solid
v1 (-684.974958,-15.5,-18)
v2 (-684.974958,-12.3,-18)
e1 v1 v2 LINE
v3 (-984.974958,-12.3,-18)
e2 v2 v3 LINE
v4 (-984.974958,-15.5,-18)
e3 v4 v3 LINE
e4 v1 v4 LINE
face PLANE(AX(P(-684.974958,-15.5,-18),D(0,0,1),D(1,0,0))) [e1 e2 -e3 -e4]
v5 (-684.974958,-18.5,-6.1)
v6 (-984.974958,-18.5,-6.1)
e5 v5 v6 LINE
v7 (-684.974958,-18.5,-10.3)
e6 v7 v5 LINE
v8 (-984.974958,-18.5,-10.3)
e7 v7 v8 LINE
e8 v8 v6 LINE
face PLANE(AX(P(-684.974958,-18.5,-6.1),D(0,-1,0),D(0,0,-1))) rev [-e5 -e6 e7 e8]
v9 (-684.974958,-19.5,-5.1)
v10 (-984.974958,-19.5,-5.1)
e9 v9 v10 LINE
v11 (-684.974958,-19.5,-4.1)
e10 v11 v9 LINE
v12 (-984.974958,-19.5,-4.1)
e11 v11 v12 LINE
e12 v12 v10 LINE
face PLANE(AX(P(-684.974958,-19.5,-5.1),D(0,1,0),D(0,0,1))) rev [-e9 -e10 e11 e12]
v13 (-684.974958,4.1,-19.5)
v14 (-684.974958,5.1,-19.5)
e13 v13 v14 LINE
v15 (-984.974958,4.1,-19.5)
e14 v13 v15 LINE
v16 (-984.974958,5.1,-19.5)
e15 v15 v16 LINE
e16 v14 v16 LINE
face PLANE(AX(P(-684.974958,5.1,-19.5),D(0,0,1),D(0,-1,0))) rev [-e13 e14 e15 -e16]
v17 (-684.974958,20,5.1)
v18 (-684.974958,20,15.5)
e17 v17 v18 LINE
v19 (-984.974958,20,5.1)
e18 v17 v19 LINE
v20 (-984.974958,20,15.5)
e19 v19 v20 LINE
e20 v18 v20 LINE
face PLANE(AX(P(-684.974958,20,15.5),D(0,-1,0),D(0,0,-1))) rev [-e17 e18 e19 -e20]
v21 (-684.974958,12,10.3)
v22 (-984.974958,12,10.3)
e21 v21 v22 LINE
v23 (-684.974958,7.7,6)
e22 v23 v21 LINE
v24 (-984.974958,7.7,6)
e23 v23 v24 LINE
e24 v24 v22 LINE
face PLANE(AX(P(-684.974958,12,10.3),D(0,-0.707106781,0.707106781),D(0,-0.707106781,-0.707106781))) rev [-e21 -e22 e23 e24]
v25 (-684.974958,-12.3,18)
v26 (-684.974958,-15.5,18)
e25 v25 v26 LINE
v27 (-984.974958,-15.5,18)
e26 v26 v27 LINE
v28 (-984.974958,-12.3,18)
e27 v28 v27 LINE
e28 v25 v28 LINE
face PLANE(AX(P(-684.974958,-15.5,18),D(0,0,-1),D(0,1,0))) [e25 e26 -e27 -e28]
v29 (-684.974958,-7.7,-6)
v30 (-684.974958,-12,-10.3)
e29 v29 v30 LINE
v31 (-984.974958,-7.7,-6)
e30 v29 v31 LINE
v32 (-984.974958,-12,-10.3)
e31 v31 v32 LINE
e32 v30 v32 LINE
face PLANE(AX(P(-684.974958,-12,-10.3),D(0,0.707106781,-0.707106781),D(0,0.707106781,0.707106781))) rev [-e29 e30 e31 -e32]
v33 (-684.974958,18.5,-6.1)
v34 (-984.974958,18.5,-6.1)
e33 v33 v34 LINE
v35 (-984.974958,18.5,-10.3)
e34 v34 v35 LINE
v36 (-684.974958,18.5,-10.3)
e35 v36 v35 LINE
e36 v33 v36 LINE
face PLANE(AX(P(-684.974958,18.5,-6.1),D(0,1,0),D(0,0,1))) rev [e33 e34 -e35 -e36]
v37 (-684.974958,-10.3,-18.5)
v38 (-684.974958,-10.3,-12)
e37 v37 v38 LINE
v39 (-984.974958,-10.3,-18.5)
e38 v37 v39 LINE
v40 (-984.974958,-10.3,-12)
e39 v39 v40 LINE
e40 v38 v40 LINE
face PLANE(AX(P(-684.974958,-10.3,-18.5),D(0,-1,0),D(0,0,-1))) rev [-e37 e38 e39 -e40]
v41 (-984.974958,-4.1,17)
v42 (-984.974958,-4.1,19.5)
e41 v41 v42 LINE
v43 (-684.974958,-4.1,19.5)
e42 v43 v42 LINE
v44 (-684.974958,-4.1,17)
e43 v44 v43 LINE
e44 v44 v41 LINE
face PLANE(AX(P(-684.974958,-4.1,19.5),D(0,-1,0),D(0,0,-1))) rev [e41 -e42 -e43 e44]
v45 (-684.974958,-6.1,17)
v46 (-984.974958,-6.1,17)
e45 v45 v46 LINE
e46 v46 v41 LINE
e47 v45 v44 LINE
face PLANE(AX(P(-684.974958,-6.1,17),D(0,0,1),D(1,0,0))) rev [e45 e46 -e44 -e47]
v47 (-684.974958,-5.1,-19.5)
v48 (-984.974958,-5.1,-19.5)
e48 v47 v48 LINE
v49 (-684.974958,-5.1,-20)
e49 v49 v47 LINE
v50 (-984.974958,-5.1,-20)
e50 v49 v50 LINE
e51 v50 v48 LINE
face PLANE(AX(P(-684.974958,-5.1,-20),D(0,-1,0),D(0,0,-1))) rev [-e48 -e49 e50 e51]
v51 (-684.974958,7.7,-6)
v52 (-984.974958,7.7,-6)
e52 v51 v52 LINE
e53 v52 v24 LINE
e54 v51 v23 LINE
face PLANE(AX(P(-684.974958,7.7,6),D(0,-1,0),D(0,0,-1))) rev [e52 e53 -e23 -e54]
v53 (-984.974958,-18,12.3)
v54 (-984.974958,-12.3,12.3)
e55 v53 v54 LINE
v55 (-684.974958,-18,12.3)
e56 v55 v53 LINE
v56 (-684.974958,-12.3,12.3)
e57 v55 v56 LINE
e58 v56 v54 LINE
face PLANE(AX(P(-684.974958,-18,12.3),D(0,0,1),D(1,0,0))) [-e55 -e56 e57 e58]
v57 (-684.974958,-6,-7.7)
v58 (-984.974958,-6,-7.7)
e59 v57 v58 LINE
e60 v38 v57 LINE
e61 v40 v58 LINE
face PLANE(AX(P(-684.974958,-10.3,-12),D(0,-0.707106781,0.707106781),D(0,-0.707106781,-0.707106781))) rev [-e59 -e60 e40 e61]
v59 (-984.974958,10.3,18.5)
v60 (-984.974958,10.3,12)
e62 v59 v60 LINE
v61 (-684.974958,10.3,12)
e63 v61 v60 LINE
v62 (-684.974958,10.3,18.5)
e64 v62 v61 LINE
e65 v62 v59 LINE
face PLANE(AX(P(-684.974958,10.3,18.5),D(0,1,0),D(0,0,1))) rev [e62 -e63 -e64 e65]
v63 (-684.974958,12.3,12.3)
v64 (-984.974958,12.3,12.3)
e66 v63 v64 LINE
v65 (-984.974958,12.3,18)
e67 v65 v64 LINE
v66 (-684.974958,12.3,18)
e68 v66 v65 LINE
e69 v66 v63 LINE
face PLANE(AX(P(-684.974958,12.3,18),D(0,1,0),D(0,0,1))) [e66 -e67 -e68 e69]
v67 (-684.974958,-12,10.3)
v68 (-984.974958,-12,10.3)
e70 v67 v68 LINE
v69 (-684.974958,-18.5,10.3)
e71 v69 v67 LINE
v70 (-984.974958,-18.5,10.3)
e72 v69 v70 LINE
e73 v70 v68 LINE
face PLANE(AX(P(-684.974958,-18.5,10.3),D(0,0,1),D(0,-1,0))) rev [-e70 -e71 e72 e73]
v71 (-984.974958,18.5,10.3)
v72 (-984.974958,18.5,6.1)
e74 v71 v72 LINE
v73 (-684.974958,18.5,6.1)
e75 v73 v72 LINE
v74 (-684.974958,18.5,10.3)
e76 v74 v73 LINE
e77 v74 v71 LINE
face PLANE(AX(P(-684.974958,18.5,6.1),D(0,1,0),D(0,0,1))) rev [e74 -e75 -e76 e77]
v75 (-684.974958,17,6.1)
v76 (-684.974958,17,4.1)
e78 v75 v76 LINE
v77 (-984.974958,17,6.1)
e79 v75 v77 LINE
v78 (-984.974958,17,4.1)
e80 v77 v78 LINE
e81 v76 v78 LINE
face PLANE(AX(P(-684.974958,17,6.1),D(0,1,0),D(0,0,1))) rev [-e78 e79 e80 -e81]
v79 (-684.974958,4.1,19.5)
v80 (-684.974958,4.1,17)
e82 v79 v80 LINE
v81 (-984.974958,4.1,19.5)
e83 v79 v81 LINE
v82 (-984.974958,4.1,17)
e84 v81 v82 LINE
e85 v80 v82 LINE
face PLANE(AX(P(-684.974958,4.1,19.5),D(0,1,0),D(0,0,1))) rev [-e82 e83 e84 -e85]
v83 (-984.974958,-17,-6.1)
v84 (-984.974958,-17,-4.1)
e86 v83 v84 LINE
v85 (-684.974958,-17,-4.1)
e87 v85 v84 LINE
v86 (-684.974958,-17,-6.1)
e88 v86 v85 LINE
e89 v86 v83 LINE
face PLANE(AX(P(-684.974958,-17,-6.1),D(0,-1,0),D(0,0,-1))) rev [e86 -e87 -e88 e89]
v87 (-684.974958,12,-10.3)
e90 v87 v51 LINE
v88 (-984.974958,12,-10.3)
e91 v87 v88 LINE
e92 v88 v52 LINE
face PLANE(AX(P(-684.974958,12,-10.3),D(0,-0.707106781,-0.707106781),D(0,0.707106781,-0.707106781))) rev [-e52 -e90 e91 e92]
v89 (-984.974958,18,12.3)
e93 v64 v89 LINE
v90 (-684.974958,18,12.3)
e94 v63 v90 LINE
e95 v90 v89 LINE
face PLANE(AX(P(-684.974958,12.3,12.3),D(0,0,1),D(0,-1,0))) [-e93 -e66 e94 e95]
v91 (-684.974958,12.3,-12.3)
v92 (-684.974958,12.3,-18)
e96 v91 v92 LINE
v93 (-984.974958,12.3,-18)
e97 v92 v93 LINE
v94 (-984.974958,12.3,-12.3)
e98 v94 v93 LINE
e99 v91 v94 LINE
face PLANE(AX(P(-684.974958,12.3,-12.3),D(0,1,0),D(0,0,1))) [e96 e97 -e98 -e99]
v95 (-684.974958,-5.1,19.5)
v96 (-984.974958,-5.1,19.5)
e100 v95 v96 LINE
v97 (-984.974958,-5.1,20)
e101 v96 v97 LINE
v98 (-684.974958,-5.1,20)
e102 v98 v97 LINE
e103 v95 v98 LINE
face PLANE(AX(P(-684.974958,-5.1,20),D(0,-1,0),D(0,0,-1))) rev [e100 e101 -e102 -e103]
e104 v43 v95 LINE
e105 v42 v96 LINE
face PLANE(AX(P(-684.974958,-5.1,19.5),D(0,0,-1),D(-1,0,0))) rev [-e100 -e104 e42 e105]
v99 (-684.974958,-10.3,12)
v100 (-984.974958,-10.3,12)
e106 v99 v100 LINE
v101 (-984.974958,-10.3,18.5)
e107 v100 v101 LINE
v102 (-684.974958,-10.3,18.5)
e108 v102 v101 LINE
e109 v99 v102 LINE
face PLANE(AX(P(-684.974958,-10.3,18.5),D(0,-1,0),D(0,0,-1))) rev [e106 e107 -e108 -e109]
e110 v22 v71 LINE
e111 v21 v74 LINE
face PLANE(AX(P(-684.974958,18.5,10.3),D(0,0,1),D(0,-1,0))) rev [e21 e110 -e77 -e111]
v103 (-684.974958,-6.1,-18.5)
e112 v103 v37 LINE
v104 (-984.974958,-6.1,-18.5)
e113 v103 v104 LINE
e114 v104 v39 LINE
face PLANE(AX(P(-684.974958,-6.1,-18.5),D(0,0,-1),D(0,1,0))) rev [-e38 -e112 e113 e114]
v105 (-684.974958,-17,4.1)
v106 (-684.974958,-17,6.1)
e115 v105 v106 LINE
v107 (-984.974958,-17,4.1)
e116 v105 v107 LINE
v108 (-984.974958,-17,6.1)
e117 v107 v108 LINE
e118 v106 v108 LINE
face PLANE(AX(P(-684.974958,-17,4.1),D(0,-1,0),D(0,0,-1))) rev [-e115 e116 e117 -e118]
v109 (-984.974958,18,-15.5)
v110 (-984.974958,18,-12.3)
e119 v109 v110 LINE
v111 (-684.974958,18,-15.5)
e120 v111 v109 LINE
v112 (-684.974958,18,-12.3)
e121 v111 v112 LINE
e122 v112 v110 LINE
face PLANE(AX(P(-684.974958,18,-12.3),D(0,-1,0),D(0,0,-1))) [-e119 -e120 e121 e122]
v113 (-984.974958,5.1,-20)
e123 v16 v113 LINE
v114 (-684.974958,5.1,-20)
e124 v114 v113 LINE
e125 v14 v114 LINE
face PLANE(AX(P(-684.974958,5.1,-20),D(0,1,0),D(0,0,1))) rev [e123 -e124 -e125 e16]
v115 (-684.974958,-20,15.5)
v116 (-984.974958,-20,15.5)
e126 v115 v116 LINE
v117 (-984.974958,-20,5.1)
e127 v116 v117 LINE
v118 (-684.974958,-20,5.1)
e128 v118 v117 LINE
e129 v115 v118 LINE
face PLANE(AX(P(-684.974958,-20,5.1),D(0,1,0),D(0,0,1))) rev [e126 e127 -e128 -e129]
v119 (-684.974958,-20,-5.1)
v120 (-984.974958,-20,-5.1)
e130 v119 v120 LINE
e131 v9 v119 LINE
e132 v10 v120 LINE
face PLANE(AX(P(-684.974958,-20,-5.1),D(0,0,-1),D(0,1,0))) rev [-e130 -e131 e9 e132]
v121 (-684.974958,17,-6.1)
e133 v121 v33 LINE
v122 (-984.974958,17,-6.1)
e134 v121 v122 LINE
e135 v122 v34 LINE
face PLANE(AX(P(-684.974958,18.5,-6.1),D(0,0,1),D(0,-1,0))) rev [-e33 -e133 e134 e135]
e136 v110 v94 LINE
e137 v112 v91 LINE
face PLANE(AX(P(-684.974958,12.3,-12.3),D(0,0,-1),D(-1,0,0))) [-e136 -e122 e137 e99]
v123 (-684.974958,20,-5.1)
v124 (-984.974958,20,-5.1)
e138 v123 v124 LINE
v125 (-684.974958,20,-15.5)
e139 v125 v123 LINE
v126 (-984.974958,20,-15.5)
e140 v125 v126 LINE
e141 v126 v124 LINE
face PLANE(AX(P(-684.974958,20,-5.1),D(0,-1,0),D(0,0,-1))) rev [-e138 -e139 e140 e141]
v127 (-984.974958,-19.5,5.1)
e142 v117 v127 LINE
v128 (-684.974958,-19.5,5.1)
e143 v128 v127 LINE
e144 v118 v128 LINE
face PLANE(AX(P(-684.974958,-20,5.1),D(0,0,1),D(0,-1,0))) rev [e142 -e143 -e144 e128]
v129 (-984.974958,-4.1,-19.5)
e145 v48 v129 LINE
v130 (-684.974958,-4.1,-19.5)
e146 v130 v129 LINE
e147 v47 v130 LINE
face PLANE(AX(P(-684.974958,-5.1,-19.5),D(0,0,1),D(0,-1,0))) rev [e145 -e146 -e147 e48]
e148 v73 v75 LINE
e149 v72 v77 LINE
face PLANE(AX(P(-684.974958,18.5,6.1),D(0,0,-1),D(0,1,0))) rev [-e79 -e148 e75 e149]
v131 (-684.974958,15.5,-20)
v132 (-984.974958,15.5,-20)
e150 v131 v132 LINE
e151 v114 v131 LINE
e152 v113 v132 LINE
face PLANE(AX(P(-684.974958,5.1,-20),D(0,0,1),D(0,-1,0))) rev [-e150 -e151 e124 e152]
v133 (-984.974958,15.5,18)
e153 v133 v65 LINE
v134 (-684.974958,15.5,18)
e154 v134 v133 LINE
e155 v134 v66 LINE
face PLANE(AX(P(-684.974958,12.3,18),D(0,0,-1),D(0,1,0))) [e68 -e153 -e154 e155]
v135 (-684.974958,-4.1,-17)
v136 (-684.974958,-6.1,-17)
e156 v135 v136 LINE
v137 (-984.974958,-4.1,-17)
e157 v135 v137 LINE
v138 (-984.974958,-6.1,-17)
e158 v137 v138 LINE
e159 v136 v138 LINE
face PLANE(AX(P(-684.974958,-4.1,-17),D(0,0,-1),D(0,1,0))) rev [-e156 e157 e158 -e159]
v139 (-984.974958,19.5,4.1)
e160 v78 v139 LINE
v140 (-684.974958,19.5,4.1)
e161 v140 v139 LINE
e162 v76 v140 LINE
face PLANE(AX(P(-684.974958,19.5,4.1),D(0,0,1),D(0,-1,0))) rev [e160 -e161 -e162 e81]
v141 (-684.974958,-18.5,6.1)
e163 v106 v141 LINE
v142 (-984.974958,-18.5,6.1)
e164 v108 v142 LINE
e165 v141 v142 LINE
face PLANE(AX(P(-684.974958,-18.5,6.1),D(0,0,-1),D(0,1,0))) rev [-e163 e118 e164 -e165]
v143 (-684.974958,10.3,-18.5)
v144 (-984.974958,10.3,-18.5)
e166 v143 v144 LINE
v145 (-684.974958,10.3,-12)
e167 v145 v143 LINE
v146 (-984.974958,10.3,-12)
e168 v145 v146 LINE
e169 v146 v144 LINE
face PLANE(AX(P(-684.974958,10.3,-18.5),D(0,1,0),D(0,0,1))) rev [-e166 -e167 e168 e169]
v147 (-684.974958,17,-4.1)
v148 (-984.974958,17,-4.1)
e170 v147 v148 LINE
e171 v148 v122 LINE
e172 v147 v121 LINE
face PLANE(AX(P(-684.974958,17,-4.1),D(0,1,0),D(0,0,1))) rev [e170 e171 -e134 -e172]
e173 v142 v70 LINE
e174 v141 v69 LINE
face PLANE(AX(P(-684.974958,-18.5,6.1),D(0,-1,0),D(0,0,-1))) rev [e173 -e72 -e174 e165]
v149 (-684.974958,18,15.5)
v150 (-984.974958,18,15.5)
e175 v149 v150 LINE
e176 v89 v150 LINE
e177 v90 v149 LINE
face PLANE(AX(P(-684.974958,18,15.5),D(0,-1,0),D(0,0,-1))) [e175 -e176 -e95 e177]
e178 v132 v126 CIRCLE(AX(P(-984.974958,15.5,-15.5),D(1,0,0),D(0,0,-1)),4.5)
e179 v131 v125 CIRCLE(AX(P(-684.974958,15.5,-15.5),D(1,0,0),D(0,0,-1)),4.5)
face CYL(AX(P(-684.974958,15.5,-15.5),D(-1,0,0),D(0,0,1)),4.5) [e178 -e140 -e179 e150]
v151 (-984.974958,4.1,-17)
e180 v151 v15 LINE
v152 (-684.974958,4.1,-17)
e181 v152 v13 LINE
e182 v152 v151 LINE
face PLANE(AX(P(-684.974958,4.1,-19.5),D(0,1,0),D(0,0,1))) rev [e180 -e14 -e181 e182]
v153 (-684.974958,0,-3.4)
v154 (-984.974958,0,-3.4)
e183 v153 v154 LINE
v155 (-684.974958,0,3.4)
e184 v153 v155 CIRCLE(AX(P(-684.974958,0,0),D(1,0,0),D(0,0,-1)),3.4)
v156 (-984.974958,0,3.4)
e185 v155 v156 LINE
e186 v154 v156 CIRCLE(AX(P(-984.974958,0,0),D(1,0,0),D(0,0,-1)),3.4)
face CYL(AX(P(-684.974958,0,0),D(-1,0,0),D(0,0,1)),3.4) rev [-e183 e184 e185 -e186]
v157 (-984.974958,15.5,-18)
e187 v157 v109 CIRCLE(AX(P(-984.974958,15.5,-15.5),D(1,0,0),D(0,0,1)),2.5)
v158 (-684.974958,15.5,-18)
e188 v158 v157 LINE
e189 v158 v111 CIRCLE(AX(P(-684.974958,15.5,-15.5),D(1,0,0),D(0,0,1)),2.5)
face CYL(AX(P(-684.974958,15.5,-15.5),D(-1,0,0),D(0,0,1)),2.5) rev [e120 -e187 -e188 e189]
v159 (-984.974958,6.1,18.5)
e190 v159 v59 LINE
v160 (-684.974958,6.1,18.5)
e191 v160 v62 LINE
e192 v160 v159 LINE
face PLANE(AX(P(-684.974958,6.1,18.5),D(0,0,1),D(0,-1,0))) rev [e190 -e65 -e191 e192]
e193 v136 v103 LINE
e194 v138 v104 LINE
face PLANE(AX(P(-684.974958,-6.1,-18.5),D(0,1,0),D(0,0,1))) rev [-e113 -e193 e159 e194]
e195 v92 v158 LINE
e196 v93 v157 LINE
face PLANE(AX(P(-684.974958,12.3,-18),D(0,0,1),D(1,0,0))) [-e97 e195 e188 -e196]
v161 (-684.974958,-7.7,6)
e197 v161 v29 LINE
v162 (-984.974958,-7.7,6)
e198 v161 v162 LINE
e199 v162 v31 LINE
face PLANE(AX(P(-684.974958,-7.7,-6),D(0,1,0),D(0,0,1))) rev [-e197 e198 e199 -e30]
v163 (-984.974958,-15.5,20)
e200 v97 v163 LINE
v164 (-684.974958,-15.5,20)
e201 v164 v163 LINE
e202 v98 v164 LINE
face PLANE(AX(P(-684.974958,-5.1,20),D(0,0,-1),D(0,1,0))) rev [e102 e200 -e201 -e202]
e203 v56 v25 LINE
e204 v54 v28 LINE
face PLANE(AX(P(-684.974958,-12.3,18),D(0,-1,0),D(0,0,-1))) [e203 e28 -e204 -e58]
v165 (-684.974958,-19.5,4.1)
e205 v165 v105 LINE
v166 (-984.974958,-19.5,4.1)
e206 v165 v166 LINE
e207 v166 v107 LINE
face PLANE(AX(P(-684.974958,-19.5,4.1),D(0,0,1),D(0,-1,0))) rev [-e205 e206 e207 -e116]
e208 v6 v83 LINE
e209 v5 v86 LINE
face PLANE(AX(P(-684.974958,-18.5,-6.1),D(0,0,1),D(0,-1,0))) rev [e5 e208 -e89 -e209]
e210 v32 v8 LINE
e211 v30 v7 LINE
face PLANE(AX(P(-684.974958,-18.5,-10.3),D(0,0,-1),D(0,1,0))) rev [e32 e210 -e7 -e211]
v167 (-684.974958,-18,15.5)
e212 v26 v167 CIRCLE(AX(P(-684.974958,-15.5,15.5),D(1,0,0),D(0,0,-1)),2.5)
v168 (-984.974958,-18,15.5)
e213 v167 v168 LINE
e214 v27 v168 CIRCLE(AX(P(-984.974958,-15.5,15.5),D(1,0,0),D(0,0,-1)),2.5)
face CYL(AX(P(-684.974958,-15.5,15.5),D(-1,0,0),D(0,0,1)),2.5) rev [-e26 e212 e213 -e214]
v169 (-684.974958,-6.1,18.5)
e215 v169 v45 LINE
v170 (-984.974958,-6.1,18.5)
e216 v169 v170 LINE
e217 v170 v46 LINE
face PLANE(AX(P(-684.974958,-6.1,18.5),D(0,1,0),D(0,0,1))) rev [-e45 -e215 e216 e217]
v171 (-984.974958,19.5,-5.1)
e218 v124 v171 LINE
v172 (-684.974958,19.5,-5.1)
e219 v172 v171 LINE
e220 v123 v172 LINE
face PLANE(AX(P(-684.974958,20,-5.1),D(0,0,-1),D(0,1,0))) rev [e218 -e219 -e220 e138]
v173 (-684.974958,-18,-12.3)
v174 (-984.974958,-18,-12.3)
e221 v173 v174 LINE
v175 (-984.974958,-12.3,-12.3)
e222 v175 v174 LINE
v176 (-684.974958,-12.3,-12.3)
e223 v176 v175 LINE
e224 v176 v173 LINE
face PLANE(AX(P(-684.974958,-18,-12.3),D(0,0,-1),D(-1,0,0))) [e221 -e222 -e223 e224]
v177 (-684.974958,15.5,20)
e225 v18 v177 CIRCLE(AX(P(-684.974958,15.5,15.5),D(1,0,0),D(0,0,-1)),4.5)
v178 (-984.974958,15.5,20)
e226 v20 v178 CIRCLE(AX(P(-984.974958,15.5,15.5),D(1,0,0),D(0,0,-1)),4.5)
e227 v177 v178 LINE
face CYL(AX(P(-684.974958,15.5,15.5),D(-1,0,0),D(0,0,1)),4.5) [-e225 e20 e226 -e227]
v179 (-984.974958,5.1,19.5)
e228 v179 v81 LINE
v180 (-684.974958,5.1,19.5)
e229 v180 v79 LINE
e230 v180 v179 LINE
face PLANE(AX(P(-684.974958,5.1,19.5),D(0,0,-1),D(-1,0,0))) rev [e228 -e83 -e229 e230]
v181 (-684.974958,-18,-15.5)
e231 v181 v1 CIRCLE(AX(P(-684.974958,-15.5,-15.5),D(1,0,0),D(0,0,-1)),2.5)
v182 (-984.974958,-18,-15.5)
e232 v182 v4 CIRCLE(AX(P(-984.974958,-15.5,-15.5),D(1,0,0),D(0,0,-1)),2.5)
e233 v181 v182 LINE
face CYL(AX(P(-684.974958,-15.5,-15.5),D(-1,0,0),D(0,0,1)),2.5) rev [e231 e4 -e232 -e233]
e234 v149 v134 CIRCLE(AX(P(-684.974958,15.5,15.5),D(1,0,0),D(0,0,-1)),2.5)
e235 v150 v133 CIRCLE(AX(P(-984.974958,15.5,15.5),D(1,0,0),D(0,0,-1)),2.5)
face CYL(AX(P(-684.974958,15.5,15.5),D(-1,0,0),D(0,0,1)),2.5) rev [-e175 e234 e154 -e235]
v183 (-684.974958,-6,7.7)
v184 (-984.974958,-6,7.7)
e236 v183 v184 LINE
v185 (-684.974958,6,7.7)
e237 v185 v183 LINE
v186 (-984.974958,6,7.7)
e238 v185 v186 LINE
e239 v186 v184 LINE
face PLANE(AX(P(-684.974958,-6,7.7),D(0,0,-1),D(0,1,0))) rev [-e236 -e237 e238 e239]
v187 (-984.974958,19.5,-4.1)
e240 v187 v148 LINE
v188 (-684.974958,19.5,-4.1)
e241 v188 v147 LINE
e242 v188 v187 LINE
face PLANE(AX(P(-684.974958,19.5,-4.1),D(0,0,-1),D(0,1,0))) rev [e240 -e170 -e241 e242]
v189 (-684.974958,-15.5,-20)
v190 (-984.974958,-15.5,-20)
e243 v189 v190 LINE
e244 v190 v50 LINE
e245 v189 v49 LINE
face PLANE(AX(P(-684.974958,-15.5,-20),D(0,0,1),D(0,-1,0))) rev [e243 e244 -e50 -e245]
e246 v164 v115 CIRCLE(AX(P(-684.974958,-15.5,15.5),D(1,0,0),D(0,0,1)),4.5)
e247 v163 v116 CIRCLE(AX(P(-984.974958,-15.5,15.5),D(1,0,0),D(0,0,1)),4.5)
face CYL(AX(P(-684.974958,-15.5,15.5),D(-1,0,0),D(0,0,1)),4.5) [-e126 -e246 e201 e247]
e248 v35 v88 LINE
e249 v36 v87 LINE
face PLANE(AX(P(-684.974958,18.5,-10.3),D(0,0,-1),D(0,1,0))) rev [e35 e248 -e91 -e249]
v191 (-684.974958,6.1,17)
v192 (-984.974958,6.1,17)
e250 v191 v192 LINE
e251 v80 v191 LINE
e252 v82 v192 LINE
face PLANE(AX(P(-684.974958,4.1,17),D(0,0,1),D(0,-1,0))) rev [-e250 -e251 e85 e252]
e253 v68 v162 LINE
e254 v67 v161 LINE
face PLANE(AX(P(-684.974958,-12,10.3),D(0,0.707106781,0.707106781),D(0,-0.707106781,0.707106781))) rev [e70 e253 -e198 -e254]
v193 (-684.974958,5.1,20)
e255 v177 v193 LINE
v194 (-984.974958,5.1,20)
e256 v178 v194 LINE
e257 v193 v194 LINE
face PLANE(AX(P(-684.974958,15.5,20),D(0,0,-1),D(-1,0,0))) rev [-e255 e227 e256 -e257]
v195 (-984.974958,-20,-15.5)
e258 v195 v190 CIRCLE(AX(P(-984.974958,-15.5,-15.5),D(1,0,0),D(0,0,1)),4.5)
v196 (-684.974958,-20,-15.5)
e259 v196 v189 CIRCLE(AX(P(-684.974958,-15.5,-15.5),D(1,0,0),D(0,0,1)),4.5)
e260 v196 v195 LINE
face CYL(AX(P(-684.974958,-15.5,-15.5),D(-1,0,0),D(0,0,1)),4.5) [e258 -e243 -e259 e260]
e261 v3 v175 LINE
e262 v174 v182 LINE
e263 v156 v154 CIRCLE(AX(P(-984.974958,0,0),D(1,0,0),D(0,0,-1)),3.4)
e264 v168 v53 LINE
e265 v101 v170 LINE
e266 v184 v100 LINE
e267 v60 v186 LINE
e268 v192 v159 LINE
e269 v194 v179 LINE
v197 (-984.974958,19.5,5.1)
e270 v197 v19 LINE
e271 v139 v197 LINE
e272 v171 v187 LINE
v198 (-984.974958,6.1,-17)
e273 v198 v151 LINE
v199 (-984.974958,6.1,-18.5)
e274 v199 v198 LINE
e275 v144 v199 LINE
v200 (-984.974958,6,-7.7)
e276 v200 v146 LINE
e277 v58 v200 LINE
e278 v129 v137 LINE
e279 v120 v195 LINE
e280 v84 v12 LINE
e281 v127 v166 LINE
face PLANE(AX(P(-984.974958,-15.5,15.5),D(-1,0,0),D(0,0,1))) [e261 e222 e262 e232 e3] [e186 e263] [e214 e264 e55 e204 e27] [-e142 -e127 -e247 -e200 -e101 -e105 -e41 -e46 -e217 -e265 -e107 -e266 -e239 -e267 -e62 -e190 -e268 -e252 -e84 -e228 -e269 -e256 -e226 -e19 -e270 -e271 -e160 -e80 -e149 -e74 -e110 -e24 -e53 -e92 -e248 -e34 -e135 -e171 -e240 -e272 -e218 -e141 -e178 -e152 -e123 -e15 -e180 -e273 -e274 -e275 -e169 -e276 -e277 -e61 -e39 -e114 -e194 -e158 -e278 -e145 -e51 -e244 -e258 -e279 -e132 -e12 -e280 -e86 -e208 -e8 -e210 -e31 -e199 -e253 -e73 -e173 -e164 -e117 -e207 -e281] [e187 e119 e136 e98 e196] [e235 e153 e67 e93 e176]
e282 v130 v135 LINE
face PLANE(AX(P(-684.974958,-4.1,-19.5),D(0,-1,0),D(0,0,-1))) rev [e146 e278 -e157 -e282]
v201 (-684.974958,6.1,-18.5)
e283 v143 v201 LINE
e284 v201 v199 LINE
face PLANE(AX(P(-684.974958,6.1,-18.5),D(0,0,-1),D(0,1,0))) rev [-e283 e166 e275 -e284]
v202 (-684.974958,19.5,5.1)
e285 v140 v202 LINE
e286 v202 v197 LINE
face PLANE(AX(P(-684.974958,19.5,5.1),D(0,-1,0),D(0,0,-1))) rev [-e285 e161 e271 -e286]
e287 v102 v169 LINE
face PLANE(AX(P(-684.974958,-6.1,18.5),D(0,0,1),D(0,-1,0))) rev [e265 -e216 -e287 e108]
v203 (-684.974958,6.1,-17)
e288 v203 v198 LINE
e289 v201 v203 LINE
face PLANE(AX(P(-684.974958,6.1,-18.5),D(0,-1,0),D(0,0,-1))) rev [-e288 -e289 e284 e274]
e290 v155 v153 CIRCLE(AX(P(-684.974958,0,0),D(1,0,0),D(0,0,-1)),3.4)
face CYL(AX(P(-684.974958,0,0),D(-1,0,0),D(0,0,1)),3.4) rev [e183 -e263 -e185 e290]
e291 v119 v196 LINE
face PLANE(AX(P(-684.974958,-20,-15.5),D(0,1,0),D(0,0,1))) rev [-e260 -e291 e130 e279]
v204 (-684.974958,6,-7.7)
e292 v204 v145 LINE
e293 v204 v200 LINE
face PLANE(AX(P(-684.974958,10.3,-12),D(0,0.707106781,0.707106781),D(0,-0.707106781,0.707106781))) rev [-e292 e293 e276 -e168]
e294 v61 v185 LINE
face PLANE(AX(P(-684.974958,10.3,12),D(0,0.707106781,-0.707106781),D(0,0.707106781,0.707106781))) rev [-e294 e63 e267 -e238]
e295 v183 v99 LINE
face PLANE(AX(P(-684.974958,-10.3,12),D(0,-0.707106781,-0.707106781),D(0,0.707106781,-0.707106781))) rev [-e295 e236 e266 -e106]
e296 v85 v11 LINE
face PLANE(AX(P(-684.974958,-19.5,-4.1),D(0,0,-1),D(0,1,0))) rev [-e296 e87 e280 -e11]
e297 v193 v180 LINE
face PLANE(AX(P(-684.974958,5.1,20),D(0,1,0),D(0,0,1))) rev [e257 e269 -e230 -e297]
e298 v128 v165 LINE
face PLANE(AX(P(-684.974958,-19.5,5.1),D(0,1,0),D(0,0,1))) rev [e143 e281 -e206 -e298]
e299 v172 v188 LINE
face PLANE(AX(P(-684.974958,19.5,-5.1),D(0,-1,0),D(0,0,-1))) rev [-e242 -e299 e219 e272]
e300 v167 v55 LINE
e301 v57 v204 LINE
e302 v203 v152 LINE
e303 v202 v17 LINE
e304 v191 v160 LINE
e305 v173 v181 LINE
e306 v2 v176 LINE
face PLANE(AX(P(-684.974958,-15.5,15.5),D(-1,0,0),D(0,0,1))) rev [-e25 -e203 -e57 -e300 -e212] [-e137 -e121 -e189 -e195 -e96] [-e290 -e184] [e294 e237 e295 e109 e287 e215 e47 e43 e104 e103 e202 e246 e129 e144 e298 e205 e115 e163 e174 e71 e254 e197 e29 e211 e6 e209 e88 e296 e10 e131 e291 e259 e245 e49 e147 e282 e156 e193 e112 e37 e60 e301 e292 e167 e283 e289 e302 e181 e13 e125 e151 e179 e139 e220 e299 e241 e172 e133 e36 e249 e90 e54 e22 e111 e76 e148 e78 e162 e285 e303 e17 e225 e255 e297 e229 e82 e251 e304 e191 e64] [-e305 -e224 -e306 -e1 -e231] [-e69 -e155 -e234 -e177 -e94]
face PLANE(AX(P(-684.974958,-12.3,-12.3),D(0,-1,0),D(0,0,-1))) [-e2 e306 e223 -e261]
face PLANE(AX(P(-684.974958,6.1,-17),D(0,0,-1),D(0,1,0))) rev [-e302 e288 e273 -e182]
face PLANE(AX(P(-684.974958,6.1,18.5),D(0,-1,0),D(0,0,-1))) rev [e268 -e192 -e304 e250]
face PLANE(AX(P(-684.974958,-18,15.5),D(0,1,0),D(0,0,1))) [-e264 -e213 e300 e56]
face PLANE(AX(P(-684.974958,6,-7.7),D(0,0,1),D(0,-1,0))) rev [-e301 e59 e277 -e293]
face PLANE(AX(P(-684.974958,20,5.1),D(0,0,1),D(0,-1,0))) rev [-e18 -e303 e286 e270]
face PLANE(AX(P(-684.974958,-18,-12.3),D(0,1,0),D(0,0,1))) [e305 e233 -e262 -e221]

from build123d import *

# Parameters (mm, degrees)
SKETCH1_R                                 = 3.4
ALUMINIUM_PROFILE_40_X_40B_X_R4_5_1_DEPTH = 300


with BuildPart() as part:
    # Sketch1 → Aluminium profile 40 X 40B X R4.5(1) (new body)
    with BuildSketch(Plane.YZ.offset(-984.974958264)):
        with BuildLine():
            Line((-5.1, 20), (-5.1, 19.5))
            Line((-5.1, 19.5), (-4.1, 19.5))
            Line((-4.1, 19.5), (-4.1, 17))
            Line((-4.1, 17), (-6.1, 17))
            Line((-6.1, 17), (-6.1, 18.5))
            Line((-6.1, 18.5), (-10.3, 18.5))
            Line((-10.3, 18.5), (-10.3, 12))
            Line((-10.3, 12), (-6, 7.7))
            Line((-6, 7.7), (6, 7.7))
            Line((6, 7.7), (10.3, 12))
            Line((10.3, 12), (10.3, 18.5))
            Line((10.3, 18.5), (6.1, 18.5))
            Line((6.1, 18.5), (6.1, 17))
            Line((6.1, 17), (4.1, 17))
            Line((4.1, 17), (4.1, 19.5))
            Line((4.1, 19.5), (5.1, 19.5))
            Line((5.1, 19.5), (5.1, 20))
            Line((5.1, 20), (15.5, 20))
            ThreePointArc((15.5, 20), (18.681980515, 18.681980515), (20, 15.5))
            Line((20, 15.5), (20, 5.1))
            Line((20, 5.1), (19.5, 5.1))
            Line((19.5, 5.1), (19.5, 4.1))
            Line((19.5, 4.1), (17, 4.1))
            Line((17, 4.1), (17, 6.1))
            Line((17, 6.1), (18.5, 6.1))
            Line((18.5, 6.1), (18.5, 10.3))
            Line((18.5, 10.3), (12, 10.3))
            Line((12, 10.3), (7.7, 6))
            Line((7.7, 6), (7.7, -6))
            Line((7.7, -6), (12, -10.3))
            Line((12, -10.3), (18.5, -10.3))
            Line((18.5, -10.3), (18.5, -6.1))
            Line((18.5, -6.1), (17, -6.1))
            Line((17, -6.1), (17, -4.1))
            Line((17, -4.1), (19.5, -4.1))
            Line((19.5, -4.1), (19.5, -5.1))
            Line((19.5, -5.1), (20, -5.1))
            Line((20, -5.1), (20, -15.5))
            ThreePointArc((20, -15.5), (18.681980515, -18.681980515), (15.5, -20))
            Line((15.5, -20), (5.1, -20))
            Line((5.1, -20), (5.1, -19.5))
            Line((5.1, -19.5), (4.1, -19.5))
            Line((4.1, -19.5), (4.1, -17))
            Line((4.1, -17), (6.1, -17))
            Line((6.1, -17), (6.1, -18.5))
            Line((6.1, -18.5), (10.3, -18.5))
            Line((10.3, -18.5), (10.3, -12))
            Line((10.3, -12), (6, -7.7))
            Line((6, -7.7), (-6, -7.7))
            Line((-6, -7.7), (-10.3, -12))
            Line((-10.3, -12), (-10.3, -18.5))
            Line((-10.3, -18.5), (-6.1, -18.5))
            Line((-6.1, -18.5), (-6.1, -17))
            Line((-6.1, -17), (-4.1, -17))
            Line((-4.1, -17), (-4.1, -19.5))
            Line((-4.1, -19.5), (-5.1, -19.5))
            Line((-5.1, -19.5), (-5.1, -20))
            Line((-5.1, -20), (-15.5, -20))
            ThreePointArc((-15.5, -20), (-18.681980515, -18.681980515), (-20, -15.5))
            Line((-20, -15.5), (-20, -5.1))
            Line((-20, -5.1), (-19.5, -5.1))
            Line((-19.5, -5.1), (-19.5, -4.1))
            Line((-19.5, -4.1), (-17, -4.1))
            Line((-17, -4.1), (-17, -6.1))
            Line((-17, -6.1), (-18.5, -6.1))
            Line((-18.5, -6.1), (-18.5, -10.3))
            Line((-18.5, -10.3), (-12, -10.3))
            Line((-12, -10.3), (-7.7, -6))
            Line((-7.7, -6), (-7.7, 6))
            Line((-7.7, 6), (-12, 10.3))
            Line((-12, 10.3), (-18.5, 10.3))
            Line((-18.5, 10.3), (-18.5, 6.1))
            Line((-18.5, 6.1), (-17, 6.1))
            Line((-17, 6.1), (-17, 4.1))
            Line((-17, 4.1), (-19.5, 4.1))
            Line((-19.5, 4.1), (-19.5, 5.1))
            Line((-19.5, 5.1), (-20, 5.1))
            Line((-20, 5.1), (-20, 15.5))
            ThreePointArc((-20, 15.5), (-18.681980515, 18.681980515), (-15.5, 20))
            Line((-15.5, 20), (-5.1, 20))
        make_face()
        Circle(SKETCH1_R, mode=Mode.SUBTRACT)
        with BuildLine():
            Line((12.3, 18), (15.5, 18))
            ThreePointArc((15.5, 18), (17.267766953, 17.267766953), (18, 15.5))
            Line((18, 15.5), (18, 12.3))
            Line((18, 12.3), (12.3, 12.3))
            Line((12.3, 12.3), (12.3, 18))
        make_face(mode=Mode.SUBTRACT)
        with BuildLine():
            Line((-15.5, 18), (-12.3, 18))
            Line((-12.3, 18), (-12.3, 12.3))
            Line((-12.3, 12.3), (-18, 12.3))
            Line((-18, 12.3), (-18, 15.5))
            ThreePointArc((-18, 15.5), (-17.267766953, 17.267766953), (-15.5, 18))
        make_face(mode=Mode.SUBTRACT)
        with BuildLine():
            Line((-18, -12.3), (-12.3, -12.3))
            Line((-12.3, -12.3), (-12.3, -18))
            Line((-12.3, -18), (-15.5, -18))
            ThreePointArc((-15.5, -18), (-17.267766953, -17.267766953), (-18, -15.5))
            Line((-18, -15.5), (-18, -12.3))
        make_face(mode=Mode.SUBTRACT)
        with BuildLine():
            Line((12.3, -12.3), (18, -12.3))
            Line((18, -12.3), (18, -15.5))
            ThreePointArc((18, -15.5), (17.267766953, -17.267766953), (15.5, -18))
            Line((15.5, -18), (12.3, -18))
            Line((12.3, -18), (12.3, -12.3))
        make_face(mode=Mode.SUBTRACT)
    extrude(amount=ALUMINIUM_PROFILE_40_X_40B_X_R4_5_1_DEPTH)


solid = part.part
